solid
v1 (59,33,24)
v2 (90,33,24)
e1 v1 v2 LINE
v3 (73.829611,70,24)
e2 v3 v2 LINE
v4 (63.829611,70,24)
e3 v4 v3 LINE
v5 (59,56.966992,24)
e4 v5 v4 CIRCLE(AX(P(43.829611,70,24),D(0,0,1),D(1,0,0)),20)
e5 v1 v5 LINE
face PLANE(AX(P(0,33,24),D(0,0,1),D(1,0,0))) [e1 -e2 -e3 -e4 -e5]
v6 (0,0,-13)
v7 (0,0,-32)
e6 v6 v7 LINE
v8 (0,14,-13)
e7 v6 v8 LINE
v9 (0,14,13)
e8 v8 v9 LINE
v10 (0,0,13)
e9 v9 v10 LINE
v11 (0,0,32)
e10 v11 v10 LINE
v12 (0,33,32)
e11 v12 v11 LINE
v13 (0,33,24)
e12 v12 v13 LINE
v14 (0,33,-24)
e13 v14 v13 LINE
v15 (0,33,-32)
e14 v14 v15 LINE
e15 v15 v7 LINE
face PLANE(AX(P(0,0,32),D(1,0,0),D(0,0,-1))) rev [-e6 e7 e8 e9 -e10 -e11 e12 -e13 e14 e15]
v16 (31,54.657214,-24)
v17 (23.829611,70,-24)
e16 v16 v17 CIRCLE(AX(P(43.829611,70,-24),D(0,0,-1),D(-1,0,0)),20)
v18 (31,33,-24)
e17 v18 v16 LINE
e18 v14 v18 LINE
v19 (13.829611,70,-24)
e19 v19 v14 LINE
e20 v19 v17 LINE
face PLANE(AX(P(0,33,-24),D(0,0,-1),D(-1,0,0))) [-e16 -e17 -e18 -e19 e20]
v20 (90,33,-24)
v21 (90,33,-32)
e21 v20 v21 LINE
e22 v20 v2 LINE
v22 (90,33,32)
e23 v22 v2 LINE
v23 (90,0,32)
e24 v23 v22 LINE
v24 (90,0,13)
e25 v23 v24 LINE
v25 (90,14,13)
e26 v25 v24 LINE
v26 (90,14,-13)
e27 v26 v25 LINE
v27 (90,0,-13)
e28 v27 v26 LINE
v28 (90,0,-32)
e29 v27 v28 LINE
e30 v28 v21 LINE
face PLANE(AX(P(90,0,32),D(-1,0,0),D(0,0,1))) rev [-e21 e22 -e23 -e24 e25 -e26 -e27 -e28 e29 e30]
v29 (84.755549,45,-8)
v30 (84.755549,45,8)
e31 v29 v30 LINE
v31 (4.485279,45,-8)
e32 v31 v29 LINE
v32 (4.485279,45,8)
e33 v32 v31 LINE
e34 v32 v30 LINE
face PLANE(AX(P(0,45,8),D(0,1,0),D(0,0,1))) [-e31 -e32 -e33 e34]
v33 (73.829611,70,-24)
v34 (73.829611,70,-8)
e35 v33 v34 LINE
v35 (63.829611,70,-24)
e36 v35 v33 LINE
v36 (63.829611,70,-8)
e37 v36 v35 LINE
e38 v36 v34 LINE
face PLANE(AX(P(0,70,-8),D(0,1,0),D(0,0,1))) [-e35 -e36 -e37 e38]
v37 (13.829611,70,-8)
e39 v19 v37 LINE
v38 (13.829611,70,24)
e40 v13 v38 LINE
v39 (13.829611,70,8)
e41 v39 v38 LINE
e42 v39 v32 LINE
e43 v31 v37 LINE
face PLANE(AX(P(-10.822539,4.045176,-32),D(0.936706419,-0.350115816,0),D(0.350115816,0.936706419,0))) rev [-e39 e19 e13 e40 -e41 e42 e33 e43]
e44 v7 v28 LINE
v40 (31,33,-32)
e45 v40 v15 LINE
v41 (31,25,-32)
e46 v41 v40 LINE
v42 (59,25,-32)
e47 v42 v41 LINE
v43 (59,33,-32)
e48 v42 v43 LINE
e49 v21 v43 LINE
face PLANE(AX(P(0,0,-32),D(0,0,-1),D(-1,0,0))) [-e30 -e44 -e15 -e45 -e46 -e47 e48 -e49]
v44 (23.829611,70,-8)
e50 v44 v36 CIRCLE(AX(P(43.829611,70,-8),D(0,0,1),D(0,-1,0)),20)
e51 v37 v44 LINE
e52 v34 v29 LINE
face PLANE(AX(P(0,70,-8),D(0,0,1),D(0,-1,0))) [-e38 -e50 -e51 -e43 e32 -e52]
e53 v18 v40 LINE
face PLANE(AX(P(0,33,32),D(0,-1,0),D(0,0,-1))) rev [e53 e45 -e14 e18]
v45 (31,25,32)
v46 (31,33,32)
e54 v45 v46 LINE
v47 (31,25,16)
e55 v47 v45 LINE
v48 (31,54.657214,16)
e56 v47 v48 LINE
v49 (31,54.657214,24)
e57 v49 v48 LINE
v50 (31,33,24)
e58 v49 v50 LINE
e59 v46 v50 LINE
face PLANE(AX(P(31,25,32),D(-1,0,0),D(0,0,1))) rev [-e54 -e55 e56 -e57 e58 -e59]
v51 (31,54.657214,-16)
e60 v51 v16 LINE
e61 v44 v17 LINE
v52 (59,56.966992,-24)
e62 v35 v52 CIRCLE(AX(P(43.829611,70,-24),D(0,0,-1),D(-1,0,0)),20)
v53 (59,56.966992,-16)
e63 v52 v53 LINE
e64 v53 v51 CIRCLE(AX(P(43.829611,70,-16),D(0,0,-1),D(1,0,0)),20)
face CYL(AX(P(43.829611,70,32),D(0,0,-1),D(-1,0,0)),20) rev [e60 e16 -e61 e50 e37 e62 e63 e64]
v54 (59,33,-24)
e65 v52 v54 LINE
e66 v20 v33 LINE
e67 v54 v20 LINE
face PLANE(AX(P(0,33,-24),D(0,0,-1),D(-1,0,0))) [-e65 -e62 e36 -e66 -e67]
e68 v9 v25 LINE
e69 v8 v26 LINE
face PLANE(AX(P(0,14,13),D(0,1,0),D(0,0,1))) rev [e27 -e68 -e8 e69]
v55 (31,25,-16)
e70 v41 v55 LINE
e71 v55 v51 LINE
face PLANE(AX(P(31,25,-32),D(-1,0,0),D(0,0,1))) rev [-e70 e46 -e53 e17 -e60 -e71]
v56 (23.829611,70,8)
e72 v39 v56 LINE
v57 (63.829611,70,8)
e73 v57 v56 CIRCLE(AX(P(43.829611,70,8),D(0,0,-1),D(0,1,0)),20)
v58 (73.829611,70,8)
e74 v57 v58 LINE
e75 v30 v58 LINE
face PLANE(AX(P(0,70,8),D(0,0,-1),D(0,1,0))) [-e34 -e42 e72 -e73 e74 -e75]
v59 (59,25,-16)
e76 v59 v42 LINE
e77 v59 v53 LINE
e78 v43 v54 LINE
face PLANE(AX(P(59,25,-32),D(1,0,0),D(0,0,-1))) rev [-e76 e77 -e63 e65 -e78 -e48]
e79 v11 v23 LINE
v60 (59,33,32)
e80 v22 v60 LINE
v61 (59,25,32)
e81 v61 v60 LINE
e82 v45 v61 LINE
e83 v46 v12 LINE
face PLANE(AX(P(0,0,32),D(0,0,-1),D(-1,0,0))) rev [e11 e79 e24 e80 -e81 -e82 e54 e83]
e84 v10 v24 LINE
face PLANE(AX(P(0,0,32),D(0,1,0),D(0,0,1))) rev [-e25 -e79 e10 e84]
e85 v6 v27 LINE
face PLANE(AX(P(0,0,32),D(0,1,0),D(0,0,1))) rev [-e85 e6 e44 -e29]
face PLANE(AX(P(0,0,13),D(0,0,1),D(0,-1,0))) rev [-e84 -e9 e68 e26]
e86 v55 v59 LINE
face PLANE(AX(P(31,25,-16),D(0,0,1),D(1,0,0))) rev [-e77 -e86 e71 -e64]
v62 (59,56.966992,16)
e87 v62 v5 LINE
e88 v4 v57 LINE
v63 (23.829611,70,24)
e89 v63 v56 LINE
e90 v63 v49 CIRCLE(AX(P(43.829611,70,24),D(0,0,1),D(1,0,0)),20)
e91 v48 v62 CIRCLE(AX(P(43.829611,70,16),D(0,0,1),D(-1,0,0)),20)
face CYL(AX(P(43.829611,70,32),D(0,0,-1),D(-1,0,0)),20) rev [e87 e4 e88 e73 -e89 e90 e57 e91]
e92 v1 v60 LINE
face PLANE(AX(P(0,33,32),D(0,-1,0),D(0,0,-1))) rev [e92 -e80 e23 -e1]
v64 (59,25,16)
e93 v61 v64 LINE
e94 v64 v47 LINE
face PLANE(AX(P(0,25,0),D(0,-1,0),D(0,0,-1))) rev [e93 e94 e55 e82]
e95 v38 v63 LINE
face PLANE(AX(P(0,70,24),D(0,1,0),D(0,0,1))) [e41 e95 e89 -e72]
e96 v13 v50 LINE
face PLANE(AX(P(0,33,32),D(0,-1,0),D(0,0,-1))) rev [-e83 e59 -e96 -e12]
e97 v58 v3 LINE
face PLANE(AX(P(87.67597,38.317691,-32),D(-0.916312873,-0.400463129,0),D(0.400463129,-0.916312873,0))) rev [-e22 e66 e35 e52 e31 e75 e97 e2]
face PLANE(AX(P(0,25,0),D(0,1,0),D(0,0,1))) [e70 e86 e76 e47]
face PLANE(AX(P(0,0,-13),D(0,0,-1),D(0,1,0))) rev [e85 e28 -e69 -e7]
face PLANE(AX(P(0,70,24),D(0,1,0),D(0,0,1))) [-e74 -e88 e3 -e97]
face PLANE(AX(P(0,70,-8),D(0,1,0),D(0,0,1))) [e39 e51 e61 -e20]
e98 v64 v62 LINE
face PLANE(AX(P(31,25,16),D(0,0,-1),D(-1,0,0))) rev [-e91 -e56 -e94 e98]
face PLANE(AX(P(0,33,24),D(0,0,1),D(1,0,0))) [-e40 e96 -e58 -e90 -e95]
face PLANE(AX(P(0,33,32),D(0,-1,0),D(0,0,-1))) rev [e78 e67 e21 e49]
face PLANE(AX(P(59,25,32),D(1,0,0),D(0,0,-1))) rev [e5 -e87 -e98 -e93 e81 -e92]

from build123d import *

# Parameters (mm, degrees)
BASE_BLOCK_SKETCH_W     = 90
BASE_BLOCK_SKETCH_H     = 33
BASE_BLOCK_DEPTH        = 32
BOTTOM_SLOT_SKETCH_W    = 26
BOTTOM_SLOT_SKETCH_H    = 14
BOTTOM_SLOT_DEPTH       = 102.05938848
SUPPORT_UPRIGHTS_DEPTH  = 90
CENTRE_RECESS_DEPTH     = 128.027556066
CRADLE_ARC_CUT_DEPTH    = 128.027556066
UPRIGHT_U_SLOT_SKETCH_W = 28
UPRIGHT_U_SLOT_SKETCH_H = 16
UPRIGHT_U_SLOT_DEPTH    = 45


with BuildPart() as part:
    # Base Block Sketch → Base Block (new, symmetric)
    with BuildSketch(Plane.XY):
        with Locations((45, 16.5)):
            Rectangle(BASE_BLOCK_SKETCH_W, BASE_BLOCK_SKETCH_H)
    extrude(amount=BASE_BLOCK_DEPTH, both=True)

    # Bottom Slot Sketch → Bottom Slot (cut, through all)
    with BuildSketch(Plane(origin=(90, 0, 0), x_dir=(0, 0, -1), z_dir=(1, 0, 0))):
        with Locations((0, 7)):
            Rectangle(BOTTOM_SLOT_SKETCH_W, BOTTOM_SLOT_SKETCH_H)
    extrude(amount=-BOTTOM_SLOT_DEPTH, mode=Mode.SUBTRACT)

    # Support Uprights Sketch → Support Uprights (add)
    with BuildSketch(Plane(origin=(90, 0, 0), x_dir=(0, 0, -1), z_dir=(1, 0, 0))):
        Polygon((-24, 33), (24, 33), (24, 70), (8, 70), (8, 45), (-8, 45), (-8, 70), (-24, 70), align=None)
    extrude(amount=-SUPPORT_UPRIGHTS_DEPTH)

    # Centre Recess Sketch → Centre Recess (cut, through all)
    with BuildSketch(Plane.XY.offset(24)):
        Polygon((90, 70), (73.829610801, 70), (90, 33), align=None)
        Polygon((0, 33), (13.829610801, 70), (0, 70), align=None)
    extrude(amount=-CENTRE_RECESS_DEPTH, mode=Mode.SUBTRACT)

    # Cradle Arc Sketch → Cradle Arc Cut (cut, through all)
    with BuildSketch(Plane(origin=(0, 0, -24), x_dir=(-1, 0, 0), z_dir=(0, 0, -1))):
        with BuildLine():
            Line((-23.829610801, 70), (-63.829610801, 70))
            ThreePointArc((-63.829610801, 70), (-43.829610801, 50), (-23.829610801, 70))
        make_face()
    extrude(amount=-CRADLE_ARC_CUT_DEPTH, mode=Mode.SUBTRACT)

    # Upright U-Slot Sketch → Upright U-Slot (cut)
    with BuildSketch(Plane(origin=(0, 70, 0), x_dir=(1, 0, 0), z_dir=(0, 1, 0))):
        with Locations((45, 24)):
            Rectangle(UPRIGHT_U_SLOT_SKETCH_W, UPRIGHT_U_SLOT_SKETCH_H)
        with Locations((45, -24)):
            Rectangle(UPRIGHT_U_SLOT_SKETCH_W, UPRIGHT_U_SLOT_SKETCH_H)
    extrude(amount=-UPRIGHT_U_SLOT_DEPTH, mode=Mode.SUBTRACT)


solid = part.part
